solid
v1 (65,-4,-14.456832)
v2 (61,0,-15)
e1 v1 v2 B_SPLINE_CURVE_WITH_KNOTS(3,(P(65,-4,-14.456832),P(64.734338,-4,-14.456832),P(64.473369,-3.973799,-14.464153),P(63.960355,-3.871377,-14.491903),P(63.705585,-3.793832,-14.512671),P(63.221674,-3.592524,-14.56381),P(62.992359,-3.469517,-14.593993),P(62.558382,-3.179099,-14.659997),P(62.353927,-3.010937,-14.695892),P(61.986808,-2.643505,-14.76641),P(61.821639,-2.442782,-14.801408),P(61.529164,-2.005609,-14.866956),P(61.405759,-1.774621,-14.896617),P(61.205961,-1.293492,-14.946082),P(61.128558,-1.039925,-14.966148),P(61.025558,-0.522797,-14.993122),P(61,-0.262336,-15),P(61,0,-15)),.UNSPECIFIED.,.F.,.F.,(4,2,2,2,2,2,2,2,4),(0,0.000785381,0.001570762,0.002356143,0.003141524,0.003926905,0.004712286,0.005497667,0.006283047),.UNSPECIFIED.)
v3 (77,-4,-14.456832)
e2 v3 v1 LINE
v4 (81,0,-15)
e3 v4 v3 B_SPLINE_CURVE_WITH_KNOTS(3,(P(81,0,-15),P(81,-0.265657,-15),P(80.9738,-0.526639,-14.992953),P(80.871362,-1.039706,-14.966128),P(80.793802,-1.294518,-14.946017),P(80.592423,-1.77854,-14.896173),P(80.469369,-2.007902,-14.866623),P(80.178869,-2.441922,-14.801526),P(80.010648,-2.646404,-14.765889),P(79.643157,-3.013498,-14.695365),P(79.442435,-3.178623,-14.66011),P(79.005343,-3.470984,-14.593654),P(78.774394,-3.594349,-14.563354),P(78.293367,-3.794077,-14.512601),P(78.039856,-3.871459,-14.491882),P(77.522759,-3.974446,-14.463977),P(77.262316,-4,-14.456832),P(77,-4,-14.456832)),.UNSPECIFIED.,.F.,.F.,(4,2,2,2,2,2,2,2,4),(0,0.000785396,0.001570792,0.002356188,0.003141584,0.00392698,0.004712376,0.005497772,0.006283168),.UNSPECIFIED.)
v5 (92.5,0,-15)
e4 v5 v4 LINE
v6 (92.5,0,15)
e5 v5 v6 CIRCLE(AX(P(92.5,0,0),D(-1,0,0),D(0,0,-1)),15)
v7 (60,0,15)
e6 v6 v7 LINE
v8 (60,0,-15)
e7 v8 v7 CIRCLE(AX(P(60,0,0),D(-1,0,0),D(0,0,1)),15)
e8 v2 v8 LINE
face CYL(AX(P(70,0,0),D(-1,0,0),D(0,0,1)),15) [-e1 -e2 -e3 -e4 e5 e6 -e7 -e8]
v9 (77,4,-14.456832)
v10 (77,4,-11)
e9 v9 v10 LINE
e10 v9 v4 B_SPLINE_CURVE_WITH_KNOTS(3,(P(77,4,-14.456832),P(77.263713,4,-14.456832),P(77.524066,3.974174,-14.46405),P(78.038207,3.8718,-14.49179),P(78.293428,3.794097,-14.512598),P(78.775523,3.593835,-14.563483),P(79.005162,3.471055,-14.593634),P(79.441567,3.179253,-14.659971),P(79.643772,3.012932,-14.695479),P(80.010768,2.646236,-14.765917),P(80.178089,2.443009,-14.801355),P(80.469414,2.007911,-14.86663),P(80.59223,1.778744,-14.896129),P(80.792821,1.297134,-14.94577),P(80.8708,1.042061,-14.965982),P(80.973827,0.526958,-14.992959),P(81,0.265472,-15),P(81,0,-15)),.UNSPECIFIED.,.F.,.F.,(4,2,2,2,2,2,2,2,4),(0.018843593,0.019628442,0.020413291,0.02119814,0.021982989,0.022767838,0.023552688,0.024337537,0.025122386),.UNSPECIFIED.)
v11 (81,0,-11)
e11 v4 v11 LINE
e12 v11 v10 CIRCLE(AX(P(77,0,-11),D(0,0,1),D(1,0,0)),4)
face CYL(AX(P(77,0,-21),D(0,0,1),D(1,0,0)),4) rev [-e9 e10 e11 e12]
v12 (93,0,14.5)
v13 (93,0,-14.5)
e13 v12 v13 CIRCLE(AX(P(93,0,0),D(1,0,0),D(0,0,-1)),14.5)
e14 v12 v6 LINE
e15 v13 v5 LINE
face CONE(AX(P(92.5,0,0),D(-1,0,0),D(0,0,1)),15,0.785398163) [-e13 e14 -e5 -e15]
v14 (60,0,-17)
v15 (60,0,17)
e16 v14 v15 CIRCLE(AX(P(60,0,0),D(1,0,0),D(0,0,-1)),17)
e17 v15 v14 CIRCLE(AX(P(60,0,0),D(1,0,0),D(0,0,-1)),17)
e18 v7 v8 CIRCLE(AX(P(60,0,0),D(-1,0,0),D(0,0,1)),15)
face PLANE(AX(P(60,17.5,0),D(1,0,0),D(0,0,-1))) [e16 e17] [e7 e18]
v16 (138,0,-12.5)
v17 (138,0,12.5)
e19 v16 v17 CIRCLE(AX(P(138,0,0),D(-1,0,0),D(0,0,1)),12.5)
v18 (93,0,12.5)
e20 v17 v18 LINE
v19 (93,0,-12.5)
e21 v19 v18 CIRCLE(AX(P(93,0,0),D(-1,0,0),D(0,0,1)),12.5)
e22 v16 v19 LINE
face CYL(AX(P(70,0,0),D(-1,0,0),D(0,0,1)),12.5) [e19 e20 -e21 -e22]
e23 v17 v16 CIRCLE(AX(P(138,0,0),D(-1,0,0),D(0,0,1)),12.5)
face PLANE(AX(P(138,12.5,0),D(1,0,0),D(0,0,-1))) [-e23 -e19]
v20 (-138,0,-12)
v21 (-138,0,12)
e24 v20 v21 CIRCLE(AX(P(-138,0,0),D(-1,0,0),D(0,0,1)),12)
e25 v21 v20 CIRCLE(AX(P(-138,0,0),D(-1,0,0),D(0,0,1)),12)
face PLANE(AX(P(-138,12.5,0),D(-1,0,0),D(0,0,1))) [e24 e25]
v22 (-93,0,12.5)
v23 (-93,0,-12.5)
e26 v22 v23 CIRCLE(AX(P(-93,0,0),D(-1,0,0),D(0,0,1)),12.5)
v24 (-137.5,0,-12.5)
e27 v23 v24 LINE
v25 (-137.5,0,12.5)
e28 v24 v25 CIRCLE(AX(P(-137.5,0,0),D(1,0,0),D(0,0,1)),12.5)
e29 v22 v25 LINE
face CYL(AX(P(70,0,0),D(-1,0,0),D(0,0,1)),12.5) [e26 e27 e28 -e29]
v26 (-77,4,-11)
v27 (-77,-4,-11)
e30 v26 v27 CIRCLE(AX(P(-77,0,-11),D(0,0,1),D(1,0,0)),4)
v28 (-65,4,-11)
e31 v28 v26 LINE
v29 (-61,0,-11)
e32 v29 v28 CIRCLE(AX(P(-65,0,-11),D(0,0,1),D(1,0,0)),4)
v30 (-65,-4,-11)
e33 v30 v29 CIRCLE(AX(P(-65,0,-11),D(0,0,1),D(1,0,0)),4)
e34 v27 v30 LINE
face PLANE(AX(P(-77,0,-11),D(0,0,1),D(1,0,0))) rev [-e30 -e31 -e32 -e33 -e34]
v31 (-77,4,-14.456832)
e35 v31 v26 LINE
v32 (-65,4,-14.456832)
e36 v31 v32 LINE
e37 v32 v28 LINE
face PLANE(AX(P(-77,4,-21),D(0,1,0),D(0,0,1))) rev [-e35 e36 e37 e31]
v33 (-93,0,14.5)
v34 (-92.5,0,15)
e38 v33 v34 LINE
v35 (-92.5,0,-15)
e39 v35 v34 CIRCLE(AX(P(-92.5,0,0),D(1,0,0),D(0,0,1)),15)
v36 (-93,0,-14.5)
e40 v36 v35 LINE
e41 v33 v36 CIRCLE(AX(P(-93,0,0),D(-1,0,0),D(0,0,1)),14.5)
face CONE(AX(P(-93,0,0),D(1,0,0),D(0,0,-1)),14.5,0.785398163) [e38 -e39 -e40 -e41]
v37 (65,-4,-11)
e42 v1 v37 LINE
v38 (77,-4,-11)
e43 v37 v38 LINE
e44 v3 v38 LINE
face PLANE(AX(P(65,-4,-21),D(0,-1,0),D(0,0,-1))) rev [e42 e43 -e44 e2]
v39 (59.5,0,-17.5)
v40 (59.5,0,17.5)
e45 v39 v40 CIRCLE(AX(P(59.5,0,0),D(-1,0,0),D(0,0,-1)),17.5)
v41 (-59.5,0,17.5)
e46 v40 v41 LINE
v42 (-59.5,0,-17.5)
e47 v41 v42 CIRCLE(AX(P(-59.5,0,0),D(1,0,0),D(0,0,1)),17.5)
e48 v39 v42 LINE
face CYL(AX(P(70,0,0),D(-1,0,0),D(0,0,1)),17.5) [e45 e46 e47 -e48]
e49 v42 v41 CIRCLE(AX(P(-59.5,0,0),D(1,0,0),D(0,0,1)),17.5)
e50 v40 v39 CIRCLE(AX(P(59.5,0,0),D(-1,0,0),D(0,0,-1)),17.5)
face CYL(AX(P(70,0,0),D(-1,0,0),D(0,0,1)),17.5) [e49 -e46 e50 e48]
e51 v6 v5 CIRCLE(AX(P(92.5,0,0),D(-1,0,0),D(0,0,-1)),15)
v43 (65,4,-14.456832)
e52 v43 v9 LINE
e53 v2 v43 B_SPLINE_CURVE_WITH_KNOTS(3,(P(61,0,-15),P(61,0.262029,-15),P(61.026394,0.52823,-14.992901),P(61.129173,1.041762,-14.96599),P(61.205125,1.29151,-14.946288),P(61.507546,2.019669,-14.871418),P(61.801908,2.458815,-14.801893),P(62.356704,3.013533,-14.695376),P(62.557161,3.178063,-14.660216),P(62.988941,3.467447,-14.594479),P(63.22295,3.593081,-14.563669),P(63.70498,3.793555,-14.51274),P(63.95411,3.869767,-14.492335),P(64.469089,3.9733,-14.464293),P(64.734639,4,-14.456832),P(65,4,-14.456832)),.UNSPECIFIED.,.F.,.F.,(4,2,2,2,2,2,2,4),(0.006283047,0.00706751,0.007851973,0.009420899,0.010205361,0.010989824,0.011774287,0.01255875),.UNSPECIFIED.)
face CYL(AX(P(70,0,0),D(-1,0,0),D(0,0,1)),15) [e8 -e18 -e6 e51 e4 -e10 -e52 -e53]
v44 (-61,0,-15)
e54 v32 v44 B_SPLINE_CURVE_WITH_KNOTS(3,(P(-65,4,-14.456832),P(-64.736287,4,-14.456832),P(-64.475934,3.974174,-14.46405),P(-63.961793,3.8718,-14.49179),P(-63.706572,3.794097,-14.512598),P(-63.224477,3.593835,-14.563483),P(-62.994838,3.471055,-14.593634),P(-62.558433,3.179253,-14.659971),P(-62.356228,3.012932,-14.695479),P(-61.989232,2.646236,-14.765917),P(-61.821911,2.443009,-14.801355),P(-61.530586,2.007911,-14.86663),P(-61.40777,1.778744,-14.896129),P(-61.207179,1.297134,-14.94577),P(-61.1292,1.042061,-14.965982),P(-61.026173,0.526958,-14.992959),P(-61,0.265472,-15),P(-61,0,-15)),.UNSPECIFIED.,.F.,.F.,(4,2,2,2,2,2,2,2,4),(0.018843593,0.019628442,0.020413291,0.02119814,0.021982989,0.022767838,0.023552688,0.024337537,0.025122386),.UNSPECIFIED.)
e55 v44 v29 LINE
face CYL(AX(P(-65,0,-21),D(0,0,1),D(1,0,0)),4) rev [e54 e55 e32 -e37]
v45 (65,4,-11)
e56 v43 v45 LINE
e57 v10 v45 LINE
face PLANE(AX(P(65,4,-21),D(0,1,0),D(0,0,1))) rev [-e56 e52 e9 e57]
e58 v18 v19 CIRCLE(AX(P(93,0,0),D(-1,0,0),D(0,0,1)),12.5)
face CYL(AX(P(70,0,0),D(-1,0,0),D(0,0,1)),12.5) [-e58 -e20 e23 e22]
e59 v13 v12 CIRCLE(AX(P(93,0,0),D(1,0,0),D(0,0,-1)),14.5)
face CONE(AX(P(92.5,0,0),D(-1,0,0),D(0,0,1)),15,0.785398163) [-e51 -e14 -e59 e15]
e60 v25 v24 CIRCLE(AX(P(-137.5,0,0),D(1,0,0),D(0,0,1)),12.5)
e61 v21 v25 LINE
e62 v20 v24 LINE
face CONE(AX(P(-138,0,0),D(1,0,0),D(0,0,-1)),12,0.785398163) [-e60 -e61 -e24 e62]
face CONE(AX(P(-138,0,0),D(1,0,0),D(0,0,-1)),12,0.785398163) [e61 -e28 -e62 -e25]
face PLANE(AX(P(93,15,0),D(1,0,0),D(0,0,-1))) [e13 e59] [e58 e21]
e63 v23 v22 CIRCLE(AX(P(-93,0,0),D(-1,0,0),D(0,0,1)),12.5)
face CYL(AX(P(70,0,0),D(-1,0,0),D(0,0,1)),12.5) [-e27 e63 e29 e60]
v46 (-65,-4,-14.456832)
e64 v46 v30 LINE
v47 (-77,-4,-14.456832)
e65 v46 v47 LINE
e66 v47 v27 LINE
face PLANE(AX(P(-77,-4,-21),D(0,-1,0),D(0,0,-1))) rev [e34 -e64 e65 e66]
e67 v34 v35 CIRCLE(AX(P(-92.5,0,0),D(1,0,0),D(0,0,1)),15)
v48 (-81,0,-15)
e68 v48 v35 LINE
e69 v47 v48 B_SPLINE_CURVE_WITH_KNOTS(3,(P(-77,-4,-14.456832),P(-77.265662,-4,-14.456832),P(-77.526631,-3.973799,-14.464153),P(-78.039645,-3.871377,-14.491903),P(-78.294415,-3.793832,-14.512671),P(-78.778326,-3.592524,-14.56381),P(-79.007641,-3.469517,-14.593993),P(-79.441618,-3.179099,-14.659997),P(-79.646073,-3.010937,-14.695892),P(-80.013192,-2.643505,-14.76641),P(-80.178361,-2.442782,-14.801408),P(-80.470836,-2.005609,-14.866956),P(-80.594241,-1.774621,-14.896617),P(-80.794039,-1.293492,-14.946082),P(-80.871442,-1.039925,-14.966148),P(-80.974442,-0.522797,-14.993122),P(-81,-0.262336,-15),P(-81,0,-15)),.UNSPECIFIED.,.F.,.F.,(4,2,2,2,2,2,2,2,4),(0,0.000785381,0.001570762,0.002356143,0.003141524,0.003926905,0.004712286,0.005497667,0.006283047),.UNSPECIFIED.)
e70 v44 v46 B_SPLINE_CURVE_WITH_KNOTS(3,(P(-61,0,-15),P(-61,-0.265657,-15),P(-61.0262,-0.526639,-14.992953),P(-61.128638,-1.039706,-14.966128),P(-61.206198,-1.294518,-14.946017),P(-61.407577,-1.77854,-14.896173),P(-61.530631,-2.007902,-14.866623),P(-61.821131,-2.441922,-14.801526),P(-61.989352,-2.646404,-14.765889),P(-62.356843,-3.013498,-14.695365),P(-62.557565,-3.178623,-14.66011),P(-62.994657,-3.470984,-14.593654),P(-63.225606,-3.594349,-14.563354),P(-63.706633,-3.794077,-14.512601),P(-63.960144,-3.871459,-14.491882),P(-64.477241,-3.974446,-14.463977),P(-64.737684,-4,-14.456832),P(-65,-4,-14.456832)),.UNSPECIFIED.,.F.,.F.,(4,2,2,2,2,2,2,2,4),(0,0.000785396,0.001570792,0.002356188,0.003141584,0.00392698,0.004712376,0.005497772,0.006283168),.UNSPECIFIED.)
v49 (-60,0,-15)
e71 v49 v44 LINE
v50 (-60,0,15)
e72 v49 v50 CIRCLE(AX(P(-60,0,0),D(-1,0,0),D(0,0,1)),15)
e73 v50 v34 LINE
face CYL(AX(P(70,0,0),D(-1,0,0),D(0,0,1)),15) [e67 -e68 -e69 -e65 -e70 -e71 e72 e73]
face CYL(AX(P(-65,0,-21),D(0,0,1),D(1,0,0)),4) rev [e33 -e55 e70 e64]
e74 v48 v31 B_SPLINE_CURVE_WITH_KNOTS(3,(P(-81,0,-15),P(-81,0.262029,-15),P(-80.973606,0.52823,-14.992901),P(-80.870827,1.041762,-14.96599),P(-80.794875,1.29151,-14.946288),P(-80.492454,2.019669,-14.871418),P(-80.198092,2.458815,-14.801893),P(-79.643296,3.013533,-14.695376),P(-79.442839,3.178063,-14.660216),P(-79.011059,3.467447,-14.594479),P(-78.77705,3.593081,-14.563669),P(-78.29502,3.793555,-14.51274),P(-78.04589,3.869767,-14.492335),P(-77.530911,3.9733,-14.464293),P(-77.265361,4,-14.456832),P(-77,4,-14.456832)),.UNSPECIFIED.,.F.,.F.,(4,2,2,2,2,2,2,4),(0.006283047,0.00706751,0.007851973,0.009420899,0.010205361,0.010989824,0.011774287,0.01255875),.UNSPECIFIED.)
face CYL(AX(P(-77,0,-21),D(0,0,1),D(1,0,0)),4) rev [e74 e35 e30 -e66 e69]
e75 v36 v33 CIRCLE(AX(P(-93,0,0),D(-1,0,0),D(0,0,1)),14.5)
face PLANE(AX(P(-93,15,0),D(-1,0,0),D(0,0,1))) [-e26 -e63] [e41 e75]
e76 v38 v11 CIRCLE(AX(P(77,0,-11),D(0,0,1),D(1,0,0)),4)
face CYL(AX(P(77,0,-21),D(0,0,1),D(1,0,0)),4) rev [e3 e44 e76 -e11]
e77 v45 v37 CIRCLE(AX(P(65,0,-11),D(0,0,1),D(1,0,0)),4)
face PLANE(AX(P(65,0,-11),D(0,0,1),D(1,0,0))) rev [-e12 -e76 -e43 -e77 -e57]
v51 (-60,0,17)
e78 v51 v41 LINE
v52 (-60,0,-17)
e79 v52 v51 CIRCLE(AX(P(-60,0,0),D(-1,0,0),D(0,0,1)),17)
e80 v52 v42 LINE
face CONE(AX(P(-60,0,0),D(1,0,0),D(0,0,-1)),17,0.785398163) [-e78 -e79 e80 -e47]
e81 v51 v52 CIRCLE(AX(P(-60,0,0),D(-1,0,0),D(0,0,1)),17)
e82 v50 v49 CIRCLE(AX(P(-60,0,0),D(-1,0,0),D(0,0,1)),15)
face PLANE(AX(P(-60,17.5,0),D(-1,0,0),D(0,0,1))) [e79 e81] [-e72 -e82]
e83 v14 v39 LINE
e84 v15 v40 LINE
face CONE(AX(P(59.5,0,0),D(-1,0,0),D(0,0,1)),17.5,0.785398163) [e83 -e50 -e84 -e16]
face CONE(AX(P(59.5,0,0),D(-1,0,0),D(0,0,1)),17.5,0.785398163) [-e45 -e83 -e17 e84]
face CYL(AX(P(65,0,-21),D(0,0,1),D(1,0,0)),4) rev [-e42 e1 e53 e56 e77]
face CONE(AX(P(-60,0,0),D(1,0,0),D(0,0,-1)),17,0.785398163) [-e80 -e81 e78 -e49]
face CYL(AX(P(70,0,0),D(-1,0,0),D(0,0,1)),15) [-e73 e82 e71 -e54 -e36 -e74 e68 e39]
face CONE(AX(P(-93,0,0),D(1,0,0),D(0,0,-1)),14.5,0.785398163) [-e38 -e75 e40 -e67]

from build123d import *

# Parameters (mm, degrees)
CHAMFER_1_SIZE      = 0.5
CUT_EXTRUDE_START   = -11
CUT_EXTRUDE_1_DEPTH = 10


with BuildPart() as part:
    # 草图1 → 旋转1 (revolve)
    with BuildSketch(Plane(origin=(0, 0, 0), x_dir=(-1, 0, 0), z_dir=(0, 0, -1)), mode=Mode.PRIVATE) as revolve_1_sk:
        Polygon((-60, 17.5), (60, 17.5), (60, 15), (93, 15), (93, 12.5), (138, 12.5), (138, 0), (-138, 0), (-138, 12.5), (-93, 12.5), (-93, 15), (-60, 15), align=None)
    revolve(revolve_1_sk.sketch.rotate(Axis((70, 0, 0), (-1, 0, 0)), 270), axis=Axis((70, 0, 0), (-1, 0, 0)))

    # 倒角1
    chamfer_1_edges = [part.edges().sort_by_distance(p)[0] for p in [
        (-138, 0, -12.5),
        (-93, 0, -15),
        (-60, 0, -17.5),
        (60, 0, -17.5),
        (93, 0, -15),
    ]]
    chamfer(chamfer_1_edges, length=CHAMFER_1_SIZE)

    # 草图2 → 切除-拉伸1 (cut)
    with BuildSketch(Plane.XY.offset(CUT_EXTRUDE_START)):
        with BuildLine():
            Line((-77, 4), (-65, 4))
            ThreePointArc((-65, 4), (-61, 0), (-65, -4))
            Line((-65, -4), (-77, -4))
            ThreePointArc((-77, -4), (-81, 0), (-77, 4))
        make_face()
        with BuildLine():
            Line((65, 4), (77, 4))
            ThreePointArc((77, 4), (81, 0), (77, -4))
            Line((77, -4), (65, -4))
            ThreePointArc((65, -4), (61, 0), (65, 4))
        make_face()
    extrude(amount=-CUT_EXTRUDE_1_DEPTH, mode=Mode.SUBTRACT)


solid = part.part
